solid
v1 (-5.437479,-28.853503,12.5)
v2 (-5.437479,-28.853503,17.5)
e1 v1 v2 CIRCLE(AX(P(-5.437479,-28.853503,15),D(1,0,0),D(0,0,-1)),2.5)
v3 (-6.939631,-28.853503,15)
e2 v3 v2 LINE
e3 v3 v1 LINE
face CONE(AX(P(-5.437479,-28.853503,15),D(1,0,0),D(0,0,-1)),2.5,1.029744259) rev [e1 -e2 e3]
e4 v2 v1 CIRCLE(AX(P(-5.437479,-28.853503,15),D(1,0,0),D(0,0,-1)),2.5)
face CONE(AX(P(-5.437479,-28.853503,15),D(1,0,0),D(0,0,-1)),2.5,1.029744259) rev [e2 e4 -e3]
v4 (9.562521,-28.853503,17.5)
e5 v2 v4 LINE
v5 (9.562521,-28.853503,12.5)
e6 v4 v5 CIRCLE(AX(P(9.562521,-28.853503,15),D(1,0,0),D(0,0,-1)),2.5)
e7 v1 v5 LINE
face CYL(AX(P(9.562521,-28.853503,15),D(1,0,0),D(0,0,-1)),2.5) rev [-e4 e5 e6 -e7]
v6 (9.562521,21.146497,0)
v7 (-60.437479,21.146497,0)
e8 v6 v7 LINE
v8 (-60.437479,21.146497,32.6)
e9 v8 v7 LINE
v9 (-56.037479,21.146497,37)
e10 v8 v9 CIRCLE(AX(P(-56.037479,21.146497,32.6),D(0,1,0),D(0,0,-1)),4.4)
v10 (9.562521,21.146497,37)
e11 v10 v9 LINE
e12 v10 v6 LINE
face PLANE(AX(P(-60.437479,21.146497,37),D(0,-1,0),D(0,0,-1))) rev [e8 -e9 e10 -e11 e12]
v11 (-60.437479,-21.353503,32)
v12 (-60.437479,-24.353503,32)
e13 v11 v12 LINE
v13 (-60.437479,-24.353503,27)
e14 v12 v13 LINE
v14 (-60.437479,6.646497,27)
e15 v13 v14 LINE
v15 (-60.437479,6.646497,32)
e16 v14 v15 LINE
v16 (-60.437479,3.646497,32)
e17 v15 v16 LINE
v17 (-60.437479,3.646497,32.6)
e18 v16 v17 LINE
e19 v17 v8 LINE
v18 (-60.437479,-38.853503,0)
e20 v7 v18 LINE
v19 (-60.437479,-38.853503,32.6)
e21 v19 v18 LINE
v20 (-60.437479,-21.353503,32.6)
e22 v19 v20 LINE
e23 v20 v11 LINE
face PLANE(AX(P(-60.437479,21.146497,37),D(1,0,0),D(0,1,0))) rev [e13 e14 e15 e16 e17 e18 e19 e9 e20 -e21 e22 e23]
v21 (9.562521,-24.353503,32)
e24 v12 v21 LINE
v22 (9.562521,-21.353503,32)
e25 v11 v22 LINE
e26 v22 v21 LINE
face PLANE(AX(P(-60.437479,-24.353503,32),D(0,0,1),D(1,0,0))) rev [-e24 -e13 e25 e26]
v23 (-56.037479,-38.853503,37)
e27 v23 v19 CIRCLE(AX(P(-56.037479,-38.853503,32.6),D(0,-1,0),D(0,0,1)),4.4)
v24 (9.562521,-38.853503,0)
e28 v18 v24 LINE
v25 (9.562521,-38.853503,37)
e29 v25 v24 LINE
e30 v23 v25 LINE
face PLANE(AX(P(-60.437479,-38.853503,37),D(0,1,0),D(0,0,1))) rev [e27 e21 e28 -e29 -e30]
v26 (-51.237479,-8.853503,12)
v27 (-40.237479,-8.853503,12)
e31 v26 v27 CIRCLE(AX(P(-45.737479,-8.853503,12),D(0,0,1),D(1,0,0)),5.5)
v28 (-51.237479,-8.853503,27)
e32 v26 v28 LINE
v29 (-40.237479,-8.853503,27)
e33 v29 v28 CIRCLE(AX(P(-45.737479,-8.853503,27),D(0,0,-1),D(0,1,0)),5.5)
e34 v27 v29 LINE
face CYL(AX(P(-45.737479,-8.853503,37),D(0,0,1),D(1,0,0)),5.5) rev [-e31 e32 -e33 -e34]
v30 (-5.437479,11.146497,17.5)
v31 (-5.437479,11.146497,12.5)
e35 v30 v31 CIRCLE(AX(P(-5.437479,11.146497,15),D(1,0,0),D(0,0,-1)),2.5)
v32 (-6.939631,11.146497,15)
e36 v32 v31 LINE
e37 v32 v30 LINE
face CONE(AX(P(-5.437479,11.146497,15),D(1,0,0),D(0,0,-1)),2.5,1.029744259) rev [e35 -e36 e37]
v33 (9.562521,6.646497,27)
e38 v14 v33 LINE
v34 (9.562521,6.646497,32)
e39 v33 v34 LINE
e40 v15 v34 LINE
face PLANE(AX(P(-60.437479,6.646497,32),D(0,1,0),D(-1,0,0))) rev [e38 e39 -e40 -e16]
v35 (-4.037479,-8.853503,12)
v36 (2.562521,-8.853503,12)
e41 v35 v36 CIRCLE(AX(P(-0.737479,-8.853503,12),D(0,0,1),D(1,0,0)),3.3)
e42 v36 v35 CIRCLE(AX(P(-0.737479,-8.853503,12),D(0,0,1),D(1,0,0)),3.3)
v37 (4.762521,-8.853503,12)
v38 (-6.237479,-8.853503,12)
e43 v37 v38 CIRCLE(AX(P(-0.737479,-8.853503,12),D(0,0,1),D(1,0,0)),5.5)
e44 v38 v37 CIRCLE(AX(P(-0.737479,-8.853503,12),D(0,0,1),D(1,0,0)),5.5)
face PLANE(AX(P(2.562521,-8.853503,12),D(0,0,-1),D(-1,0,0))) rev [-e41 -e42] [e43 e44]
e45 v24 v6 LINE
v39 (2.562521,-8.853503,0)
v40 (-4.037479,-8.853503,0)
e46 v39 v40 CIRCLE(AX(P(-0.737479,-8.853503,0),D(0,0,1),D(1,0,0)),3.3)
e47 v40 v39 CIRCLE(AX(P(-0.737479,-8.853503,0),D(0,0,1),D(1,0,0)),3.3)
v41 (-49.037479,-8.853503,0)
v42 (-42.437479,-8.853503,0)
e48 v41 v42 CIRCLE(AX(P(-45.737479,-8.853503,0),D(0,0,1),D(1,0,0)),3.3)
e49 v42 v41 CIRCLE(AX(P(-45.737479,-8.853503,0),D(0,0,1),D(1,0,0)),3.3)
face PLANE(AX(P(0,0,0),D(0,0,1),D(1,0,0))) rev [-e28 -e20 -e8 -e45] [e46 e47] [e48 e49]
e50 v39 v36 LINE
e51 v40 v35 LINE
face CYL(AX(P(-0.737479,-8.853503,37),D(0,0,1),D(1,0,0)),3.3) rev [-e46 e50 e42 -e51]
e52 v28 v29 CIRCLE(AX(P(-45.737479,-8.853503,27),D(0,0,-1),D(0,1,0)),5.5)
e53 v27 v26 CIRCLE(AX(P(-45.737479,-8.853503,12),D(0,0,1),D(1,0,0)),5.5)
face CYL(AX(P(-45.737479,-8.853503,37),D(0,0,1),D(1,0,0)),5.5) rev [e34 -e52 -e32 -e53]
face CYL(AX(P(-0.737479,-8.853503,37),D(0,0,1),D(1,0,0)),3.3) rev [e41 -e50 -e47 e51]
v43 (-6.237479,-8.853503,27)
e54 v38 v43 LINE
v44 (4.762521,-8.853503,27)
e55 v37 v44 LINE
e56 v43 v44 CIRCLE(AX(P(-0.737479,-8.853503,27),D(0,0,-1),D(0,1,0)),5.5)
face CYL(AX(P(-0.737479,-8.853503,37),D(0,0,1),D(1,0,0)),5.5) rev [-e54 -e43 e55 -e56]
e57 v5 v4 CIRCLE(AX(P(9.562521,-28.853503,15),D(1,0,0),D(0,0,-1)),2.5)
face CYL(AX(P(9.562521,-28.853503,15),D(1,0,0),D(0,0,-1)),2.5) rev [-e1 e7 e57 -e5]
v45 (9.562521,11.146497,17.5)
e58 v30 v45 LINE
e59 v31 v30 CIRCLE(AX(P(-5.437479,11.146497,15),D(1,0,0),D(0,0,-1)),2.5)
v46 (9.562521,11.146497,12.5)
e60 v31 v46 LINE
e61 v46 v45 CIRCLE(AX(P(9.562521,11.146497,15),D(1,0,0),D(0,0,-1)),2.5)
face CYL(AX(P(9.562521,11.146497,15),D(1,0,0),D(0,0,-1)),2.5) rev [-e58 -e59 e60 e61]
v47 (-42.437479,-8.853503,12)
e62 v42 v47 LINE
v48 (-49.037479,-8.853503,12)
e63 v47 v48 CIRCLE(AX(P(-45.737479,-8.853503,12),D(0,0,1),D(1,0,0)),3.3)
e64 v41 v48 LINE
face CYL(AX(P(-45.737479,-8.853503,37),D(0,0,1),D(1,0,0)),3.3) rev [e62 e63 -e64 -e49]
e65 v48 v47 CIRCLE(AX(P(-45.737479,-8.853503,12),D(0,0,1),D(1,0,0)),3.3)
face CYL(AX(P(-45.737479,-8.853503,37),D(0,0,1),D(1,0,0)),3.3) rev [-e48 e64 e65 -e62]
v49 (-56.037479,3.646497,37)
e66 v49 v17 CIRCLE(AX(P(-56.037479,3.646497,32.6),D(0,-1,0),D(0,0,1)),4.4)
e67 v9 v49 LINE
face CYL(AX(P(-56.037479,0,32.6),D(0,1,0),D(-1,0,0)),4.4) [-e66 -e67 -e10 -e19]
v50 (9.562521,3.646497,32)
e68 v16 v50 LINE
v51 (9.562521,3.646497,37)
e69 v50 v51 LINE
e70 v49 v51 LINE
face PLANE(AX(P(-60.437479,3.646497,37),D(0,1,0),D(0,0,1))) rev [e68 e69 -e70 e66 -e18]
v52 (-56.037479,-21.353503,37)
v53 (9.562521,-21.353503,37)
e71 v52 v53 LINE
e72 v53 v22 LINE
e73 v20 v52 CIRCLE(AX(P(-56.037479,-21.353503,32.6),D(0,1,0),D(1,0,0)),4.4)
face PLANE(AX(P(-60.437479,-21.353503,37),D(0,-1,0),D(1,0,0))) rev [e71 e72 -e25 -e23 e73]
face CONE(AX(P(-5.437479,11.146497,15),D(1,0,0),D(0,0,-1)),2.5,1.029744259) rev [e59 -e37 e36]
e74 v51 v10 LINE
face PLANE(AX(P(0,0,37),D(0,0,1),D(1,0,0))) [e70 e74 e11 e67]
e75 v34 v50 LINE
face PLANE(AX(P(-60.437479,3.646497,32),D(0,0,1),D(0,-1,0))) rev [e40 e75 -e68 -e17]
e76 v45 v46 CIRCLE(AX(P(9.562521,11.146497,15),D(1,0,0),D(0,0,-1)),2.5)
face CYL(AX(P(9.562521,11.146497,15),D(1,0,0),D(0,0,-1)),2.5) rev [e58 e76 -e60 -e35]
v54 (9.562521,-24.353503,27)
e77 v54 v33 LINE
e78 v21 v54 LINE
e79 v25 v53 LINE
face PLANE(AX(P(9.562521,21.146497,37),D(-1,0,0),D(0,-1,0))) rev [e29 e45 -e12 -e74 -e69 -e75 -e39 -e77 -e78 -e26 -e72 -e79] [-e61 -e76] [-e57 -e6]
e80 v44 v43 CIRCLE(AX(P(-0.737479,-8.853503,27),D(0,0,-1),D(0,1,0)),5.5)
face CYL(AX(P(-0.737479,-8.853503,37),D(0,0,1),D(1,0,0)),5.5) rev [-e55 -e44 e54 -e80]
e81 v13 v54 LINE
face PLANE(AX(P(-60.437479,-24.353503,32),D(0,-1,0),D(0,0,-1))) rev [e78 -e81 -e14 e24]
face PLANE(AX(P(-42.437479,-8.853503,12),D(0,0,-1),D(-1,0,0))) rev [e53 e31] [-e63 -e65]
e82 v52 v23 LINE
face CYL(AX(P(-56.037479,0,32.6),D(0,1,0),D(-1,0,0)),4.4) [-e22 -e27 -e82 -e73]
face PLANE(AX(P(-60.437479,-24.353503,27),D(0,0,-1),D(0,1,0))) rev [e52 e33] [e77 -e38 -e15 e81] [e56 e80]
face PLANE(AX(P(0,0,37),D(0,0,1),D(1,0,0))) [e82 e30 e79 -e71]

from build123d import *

# Parameters (mm, degrees)
SKETCH1_W                                           = 70
SKETCH1_H                                           = 60
BOSS_EXTRUDE1_DEPTH                                 = 37
CUT_EXTRUDE2_DEPTH                                  = 89.196341816
M6_TAPPED_HOLE1_D                                   = 5
M6_TAPPED_HOLE1_DEPTH                               = 15
M6_TAPPED_HOLE1_TIP                                 = 1.502151548
FILLET1_R                                           = 4.4
CBORE_FOR_M6_HEX_SOCKET_HEAD_CAP_SCREW1_D           = 6.6
CBORE_FOR_M6_HEX_SOCKET_HEAD_CAP_SCREW1_CBORE_D     = 11
CBORE_FOR_M6_HEX_SOCKET_HEAD_CAP_SCREW1_CBORE_DEPTH = 25


with BuildPart() as part:
    # Sketch1 → Boss-Extrude1 (new body)
    with BuildSketch(Plane.XY):
        with Locations((-25.437479048, -8.853503185)):
            Rectangle(SKETCH1_W, SKETCH1_H)
    extrude(amount=BOSS_EXTRUDE1_DEPTH)

    # Sketch3 → Cut-Extrude2 (cut, through all)
    with BuildSketch(Plane(origin=(9.562520952, 0, 0), x_dir=(0, 0, -1), z_dir=(1, 0, 0))):
        Polygon((-32, -24.353503185), (-27, -24.353503185), (-27, 6.646496815), (-32, 6.646496815), (-32, 3.646496815), (-37, 3.646496815), (-37, -21.353503185), (-32, -21.353503185), align=None)
    extrude(amount=-CUT_EXTRUDE2_DEPTH, mode=Mode.SUBTRACT)

    # M6 Tapped Hole1
    with Locations(Plane(origin=(9.562520952, 0, 0), x_dir=(0, 0, -1), z_dir=(1, 0, 0))):
        with Locations((-15, -28.853503185), (-15, 11.146496815)):
            Hole(M6_TAPPED_HOLE1_D / 2, depth=M6_TAPPED_HOLE1_DEPTH)
            with Locations((0, 0, -(M6_TAPPED_HOLE1_DEPTH + M6_TAPPED_HOLE1_TIP / 2))):  # 118° drill point
                Cone(0, M6_TAPPED_HOLE1_D / 2, M6_TAPPED_HOLE1_TIP, mode=Mode.SUBTRACT)

    # Fillet1
    fillet1_edges = [part.edges().sort_by_distance(p)[0] for p in [
        (-60.437479048, -30.103503185, 37),
        (-60.437479048, 12.396496815, 37),
    ]]
    fillet(fillet1_edges, radius=FILLET1_R)

    # CBORE for M6 Hex Socket Head Cap Screw1 (through all)
    with Locations(Plane.XY.offset(37)):
        with Locations((-0.737479048, -8.853503185), (-45.737479048, -8.853503185)):
            CounterBoreHole(CBORE_FOR_M6_HEX_SOCKET_HEAD_CAP_SCREW1_D / 2, CBORE_FOR_M6_HEX_SOCKET_HEAD_CAP_SCREW1_CBORE_D / 2, CBORE_FOR_M6_HEX_SOCKET_HEAD_CAP_SCREW1_CBORE_DEPTH)


solid = part.part
